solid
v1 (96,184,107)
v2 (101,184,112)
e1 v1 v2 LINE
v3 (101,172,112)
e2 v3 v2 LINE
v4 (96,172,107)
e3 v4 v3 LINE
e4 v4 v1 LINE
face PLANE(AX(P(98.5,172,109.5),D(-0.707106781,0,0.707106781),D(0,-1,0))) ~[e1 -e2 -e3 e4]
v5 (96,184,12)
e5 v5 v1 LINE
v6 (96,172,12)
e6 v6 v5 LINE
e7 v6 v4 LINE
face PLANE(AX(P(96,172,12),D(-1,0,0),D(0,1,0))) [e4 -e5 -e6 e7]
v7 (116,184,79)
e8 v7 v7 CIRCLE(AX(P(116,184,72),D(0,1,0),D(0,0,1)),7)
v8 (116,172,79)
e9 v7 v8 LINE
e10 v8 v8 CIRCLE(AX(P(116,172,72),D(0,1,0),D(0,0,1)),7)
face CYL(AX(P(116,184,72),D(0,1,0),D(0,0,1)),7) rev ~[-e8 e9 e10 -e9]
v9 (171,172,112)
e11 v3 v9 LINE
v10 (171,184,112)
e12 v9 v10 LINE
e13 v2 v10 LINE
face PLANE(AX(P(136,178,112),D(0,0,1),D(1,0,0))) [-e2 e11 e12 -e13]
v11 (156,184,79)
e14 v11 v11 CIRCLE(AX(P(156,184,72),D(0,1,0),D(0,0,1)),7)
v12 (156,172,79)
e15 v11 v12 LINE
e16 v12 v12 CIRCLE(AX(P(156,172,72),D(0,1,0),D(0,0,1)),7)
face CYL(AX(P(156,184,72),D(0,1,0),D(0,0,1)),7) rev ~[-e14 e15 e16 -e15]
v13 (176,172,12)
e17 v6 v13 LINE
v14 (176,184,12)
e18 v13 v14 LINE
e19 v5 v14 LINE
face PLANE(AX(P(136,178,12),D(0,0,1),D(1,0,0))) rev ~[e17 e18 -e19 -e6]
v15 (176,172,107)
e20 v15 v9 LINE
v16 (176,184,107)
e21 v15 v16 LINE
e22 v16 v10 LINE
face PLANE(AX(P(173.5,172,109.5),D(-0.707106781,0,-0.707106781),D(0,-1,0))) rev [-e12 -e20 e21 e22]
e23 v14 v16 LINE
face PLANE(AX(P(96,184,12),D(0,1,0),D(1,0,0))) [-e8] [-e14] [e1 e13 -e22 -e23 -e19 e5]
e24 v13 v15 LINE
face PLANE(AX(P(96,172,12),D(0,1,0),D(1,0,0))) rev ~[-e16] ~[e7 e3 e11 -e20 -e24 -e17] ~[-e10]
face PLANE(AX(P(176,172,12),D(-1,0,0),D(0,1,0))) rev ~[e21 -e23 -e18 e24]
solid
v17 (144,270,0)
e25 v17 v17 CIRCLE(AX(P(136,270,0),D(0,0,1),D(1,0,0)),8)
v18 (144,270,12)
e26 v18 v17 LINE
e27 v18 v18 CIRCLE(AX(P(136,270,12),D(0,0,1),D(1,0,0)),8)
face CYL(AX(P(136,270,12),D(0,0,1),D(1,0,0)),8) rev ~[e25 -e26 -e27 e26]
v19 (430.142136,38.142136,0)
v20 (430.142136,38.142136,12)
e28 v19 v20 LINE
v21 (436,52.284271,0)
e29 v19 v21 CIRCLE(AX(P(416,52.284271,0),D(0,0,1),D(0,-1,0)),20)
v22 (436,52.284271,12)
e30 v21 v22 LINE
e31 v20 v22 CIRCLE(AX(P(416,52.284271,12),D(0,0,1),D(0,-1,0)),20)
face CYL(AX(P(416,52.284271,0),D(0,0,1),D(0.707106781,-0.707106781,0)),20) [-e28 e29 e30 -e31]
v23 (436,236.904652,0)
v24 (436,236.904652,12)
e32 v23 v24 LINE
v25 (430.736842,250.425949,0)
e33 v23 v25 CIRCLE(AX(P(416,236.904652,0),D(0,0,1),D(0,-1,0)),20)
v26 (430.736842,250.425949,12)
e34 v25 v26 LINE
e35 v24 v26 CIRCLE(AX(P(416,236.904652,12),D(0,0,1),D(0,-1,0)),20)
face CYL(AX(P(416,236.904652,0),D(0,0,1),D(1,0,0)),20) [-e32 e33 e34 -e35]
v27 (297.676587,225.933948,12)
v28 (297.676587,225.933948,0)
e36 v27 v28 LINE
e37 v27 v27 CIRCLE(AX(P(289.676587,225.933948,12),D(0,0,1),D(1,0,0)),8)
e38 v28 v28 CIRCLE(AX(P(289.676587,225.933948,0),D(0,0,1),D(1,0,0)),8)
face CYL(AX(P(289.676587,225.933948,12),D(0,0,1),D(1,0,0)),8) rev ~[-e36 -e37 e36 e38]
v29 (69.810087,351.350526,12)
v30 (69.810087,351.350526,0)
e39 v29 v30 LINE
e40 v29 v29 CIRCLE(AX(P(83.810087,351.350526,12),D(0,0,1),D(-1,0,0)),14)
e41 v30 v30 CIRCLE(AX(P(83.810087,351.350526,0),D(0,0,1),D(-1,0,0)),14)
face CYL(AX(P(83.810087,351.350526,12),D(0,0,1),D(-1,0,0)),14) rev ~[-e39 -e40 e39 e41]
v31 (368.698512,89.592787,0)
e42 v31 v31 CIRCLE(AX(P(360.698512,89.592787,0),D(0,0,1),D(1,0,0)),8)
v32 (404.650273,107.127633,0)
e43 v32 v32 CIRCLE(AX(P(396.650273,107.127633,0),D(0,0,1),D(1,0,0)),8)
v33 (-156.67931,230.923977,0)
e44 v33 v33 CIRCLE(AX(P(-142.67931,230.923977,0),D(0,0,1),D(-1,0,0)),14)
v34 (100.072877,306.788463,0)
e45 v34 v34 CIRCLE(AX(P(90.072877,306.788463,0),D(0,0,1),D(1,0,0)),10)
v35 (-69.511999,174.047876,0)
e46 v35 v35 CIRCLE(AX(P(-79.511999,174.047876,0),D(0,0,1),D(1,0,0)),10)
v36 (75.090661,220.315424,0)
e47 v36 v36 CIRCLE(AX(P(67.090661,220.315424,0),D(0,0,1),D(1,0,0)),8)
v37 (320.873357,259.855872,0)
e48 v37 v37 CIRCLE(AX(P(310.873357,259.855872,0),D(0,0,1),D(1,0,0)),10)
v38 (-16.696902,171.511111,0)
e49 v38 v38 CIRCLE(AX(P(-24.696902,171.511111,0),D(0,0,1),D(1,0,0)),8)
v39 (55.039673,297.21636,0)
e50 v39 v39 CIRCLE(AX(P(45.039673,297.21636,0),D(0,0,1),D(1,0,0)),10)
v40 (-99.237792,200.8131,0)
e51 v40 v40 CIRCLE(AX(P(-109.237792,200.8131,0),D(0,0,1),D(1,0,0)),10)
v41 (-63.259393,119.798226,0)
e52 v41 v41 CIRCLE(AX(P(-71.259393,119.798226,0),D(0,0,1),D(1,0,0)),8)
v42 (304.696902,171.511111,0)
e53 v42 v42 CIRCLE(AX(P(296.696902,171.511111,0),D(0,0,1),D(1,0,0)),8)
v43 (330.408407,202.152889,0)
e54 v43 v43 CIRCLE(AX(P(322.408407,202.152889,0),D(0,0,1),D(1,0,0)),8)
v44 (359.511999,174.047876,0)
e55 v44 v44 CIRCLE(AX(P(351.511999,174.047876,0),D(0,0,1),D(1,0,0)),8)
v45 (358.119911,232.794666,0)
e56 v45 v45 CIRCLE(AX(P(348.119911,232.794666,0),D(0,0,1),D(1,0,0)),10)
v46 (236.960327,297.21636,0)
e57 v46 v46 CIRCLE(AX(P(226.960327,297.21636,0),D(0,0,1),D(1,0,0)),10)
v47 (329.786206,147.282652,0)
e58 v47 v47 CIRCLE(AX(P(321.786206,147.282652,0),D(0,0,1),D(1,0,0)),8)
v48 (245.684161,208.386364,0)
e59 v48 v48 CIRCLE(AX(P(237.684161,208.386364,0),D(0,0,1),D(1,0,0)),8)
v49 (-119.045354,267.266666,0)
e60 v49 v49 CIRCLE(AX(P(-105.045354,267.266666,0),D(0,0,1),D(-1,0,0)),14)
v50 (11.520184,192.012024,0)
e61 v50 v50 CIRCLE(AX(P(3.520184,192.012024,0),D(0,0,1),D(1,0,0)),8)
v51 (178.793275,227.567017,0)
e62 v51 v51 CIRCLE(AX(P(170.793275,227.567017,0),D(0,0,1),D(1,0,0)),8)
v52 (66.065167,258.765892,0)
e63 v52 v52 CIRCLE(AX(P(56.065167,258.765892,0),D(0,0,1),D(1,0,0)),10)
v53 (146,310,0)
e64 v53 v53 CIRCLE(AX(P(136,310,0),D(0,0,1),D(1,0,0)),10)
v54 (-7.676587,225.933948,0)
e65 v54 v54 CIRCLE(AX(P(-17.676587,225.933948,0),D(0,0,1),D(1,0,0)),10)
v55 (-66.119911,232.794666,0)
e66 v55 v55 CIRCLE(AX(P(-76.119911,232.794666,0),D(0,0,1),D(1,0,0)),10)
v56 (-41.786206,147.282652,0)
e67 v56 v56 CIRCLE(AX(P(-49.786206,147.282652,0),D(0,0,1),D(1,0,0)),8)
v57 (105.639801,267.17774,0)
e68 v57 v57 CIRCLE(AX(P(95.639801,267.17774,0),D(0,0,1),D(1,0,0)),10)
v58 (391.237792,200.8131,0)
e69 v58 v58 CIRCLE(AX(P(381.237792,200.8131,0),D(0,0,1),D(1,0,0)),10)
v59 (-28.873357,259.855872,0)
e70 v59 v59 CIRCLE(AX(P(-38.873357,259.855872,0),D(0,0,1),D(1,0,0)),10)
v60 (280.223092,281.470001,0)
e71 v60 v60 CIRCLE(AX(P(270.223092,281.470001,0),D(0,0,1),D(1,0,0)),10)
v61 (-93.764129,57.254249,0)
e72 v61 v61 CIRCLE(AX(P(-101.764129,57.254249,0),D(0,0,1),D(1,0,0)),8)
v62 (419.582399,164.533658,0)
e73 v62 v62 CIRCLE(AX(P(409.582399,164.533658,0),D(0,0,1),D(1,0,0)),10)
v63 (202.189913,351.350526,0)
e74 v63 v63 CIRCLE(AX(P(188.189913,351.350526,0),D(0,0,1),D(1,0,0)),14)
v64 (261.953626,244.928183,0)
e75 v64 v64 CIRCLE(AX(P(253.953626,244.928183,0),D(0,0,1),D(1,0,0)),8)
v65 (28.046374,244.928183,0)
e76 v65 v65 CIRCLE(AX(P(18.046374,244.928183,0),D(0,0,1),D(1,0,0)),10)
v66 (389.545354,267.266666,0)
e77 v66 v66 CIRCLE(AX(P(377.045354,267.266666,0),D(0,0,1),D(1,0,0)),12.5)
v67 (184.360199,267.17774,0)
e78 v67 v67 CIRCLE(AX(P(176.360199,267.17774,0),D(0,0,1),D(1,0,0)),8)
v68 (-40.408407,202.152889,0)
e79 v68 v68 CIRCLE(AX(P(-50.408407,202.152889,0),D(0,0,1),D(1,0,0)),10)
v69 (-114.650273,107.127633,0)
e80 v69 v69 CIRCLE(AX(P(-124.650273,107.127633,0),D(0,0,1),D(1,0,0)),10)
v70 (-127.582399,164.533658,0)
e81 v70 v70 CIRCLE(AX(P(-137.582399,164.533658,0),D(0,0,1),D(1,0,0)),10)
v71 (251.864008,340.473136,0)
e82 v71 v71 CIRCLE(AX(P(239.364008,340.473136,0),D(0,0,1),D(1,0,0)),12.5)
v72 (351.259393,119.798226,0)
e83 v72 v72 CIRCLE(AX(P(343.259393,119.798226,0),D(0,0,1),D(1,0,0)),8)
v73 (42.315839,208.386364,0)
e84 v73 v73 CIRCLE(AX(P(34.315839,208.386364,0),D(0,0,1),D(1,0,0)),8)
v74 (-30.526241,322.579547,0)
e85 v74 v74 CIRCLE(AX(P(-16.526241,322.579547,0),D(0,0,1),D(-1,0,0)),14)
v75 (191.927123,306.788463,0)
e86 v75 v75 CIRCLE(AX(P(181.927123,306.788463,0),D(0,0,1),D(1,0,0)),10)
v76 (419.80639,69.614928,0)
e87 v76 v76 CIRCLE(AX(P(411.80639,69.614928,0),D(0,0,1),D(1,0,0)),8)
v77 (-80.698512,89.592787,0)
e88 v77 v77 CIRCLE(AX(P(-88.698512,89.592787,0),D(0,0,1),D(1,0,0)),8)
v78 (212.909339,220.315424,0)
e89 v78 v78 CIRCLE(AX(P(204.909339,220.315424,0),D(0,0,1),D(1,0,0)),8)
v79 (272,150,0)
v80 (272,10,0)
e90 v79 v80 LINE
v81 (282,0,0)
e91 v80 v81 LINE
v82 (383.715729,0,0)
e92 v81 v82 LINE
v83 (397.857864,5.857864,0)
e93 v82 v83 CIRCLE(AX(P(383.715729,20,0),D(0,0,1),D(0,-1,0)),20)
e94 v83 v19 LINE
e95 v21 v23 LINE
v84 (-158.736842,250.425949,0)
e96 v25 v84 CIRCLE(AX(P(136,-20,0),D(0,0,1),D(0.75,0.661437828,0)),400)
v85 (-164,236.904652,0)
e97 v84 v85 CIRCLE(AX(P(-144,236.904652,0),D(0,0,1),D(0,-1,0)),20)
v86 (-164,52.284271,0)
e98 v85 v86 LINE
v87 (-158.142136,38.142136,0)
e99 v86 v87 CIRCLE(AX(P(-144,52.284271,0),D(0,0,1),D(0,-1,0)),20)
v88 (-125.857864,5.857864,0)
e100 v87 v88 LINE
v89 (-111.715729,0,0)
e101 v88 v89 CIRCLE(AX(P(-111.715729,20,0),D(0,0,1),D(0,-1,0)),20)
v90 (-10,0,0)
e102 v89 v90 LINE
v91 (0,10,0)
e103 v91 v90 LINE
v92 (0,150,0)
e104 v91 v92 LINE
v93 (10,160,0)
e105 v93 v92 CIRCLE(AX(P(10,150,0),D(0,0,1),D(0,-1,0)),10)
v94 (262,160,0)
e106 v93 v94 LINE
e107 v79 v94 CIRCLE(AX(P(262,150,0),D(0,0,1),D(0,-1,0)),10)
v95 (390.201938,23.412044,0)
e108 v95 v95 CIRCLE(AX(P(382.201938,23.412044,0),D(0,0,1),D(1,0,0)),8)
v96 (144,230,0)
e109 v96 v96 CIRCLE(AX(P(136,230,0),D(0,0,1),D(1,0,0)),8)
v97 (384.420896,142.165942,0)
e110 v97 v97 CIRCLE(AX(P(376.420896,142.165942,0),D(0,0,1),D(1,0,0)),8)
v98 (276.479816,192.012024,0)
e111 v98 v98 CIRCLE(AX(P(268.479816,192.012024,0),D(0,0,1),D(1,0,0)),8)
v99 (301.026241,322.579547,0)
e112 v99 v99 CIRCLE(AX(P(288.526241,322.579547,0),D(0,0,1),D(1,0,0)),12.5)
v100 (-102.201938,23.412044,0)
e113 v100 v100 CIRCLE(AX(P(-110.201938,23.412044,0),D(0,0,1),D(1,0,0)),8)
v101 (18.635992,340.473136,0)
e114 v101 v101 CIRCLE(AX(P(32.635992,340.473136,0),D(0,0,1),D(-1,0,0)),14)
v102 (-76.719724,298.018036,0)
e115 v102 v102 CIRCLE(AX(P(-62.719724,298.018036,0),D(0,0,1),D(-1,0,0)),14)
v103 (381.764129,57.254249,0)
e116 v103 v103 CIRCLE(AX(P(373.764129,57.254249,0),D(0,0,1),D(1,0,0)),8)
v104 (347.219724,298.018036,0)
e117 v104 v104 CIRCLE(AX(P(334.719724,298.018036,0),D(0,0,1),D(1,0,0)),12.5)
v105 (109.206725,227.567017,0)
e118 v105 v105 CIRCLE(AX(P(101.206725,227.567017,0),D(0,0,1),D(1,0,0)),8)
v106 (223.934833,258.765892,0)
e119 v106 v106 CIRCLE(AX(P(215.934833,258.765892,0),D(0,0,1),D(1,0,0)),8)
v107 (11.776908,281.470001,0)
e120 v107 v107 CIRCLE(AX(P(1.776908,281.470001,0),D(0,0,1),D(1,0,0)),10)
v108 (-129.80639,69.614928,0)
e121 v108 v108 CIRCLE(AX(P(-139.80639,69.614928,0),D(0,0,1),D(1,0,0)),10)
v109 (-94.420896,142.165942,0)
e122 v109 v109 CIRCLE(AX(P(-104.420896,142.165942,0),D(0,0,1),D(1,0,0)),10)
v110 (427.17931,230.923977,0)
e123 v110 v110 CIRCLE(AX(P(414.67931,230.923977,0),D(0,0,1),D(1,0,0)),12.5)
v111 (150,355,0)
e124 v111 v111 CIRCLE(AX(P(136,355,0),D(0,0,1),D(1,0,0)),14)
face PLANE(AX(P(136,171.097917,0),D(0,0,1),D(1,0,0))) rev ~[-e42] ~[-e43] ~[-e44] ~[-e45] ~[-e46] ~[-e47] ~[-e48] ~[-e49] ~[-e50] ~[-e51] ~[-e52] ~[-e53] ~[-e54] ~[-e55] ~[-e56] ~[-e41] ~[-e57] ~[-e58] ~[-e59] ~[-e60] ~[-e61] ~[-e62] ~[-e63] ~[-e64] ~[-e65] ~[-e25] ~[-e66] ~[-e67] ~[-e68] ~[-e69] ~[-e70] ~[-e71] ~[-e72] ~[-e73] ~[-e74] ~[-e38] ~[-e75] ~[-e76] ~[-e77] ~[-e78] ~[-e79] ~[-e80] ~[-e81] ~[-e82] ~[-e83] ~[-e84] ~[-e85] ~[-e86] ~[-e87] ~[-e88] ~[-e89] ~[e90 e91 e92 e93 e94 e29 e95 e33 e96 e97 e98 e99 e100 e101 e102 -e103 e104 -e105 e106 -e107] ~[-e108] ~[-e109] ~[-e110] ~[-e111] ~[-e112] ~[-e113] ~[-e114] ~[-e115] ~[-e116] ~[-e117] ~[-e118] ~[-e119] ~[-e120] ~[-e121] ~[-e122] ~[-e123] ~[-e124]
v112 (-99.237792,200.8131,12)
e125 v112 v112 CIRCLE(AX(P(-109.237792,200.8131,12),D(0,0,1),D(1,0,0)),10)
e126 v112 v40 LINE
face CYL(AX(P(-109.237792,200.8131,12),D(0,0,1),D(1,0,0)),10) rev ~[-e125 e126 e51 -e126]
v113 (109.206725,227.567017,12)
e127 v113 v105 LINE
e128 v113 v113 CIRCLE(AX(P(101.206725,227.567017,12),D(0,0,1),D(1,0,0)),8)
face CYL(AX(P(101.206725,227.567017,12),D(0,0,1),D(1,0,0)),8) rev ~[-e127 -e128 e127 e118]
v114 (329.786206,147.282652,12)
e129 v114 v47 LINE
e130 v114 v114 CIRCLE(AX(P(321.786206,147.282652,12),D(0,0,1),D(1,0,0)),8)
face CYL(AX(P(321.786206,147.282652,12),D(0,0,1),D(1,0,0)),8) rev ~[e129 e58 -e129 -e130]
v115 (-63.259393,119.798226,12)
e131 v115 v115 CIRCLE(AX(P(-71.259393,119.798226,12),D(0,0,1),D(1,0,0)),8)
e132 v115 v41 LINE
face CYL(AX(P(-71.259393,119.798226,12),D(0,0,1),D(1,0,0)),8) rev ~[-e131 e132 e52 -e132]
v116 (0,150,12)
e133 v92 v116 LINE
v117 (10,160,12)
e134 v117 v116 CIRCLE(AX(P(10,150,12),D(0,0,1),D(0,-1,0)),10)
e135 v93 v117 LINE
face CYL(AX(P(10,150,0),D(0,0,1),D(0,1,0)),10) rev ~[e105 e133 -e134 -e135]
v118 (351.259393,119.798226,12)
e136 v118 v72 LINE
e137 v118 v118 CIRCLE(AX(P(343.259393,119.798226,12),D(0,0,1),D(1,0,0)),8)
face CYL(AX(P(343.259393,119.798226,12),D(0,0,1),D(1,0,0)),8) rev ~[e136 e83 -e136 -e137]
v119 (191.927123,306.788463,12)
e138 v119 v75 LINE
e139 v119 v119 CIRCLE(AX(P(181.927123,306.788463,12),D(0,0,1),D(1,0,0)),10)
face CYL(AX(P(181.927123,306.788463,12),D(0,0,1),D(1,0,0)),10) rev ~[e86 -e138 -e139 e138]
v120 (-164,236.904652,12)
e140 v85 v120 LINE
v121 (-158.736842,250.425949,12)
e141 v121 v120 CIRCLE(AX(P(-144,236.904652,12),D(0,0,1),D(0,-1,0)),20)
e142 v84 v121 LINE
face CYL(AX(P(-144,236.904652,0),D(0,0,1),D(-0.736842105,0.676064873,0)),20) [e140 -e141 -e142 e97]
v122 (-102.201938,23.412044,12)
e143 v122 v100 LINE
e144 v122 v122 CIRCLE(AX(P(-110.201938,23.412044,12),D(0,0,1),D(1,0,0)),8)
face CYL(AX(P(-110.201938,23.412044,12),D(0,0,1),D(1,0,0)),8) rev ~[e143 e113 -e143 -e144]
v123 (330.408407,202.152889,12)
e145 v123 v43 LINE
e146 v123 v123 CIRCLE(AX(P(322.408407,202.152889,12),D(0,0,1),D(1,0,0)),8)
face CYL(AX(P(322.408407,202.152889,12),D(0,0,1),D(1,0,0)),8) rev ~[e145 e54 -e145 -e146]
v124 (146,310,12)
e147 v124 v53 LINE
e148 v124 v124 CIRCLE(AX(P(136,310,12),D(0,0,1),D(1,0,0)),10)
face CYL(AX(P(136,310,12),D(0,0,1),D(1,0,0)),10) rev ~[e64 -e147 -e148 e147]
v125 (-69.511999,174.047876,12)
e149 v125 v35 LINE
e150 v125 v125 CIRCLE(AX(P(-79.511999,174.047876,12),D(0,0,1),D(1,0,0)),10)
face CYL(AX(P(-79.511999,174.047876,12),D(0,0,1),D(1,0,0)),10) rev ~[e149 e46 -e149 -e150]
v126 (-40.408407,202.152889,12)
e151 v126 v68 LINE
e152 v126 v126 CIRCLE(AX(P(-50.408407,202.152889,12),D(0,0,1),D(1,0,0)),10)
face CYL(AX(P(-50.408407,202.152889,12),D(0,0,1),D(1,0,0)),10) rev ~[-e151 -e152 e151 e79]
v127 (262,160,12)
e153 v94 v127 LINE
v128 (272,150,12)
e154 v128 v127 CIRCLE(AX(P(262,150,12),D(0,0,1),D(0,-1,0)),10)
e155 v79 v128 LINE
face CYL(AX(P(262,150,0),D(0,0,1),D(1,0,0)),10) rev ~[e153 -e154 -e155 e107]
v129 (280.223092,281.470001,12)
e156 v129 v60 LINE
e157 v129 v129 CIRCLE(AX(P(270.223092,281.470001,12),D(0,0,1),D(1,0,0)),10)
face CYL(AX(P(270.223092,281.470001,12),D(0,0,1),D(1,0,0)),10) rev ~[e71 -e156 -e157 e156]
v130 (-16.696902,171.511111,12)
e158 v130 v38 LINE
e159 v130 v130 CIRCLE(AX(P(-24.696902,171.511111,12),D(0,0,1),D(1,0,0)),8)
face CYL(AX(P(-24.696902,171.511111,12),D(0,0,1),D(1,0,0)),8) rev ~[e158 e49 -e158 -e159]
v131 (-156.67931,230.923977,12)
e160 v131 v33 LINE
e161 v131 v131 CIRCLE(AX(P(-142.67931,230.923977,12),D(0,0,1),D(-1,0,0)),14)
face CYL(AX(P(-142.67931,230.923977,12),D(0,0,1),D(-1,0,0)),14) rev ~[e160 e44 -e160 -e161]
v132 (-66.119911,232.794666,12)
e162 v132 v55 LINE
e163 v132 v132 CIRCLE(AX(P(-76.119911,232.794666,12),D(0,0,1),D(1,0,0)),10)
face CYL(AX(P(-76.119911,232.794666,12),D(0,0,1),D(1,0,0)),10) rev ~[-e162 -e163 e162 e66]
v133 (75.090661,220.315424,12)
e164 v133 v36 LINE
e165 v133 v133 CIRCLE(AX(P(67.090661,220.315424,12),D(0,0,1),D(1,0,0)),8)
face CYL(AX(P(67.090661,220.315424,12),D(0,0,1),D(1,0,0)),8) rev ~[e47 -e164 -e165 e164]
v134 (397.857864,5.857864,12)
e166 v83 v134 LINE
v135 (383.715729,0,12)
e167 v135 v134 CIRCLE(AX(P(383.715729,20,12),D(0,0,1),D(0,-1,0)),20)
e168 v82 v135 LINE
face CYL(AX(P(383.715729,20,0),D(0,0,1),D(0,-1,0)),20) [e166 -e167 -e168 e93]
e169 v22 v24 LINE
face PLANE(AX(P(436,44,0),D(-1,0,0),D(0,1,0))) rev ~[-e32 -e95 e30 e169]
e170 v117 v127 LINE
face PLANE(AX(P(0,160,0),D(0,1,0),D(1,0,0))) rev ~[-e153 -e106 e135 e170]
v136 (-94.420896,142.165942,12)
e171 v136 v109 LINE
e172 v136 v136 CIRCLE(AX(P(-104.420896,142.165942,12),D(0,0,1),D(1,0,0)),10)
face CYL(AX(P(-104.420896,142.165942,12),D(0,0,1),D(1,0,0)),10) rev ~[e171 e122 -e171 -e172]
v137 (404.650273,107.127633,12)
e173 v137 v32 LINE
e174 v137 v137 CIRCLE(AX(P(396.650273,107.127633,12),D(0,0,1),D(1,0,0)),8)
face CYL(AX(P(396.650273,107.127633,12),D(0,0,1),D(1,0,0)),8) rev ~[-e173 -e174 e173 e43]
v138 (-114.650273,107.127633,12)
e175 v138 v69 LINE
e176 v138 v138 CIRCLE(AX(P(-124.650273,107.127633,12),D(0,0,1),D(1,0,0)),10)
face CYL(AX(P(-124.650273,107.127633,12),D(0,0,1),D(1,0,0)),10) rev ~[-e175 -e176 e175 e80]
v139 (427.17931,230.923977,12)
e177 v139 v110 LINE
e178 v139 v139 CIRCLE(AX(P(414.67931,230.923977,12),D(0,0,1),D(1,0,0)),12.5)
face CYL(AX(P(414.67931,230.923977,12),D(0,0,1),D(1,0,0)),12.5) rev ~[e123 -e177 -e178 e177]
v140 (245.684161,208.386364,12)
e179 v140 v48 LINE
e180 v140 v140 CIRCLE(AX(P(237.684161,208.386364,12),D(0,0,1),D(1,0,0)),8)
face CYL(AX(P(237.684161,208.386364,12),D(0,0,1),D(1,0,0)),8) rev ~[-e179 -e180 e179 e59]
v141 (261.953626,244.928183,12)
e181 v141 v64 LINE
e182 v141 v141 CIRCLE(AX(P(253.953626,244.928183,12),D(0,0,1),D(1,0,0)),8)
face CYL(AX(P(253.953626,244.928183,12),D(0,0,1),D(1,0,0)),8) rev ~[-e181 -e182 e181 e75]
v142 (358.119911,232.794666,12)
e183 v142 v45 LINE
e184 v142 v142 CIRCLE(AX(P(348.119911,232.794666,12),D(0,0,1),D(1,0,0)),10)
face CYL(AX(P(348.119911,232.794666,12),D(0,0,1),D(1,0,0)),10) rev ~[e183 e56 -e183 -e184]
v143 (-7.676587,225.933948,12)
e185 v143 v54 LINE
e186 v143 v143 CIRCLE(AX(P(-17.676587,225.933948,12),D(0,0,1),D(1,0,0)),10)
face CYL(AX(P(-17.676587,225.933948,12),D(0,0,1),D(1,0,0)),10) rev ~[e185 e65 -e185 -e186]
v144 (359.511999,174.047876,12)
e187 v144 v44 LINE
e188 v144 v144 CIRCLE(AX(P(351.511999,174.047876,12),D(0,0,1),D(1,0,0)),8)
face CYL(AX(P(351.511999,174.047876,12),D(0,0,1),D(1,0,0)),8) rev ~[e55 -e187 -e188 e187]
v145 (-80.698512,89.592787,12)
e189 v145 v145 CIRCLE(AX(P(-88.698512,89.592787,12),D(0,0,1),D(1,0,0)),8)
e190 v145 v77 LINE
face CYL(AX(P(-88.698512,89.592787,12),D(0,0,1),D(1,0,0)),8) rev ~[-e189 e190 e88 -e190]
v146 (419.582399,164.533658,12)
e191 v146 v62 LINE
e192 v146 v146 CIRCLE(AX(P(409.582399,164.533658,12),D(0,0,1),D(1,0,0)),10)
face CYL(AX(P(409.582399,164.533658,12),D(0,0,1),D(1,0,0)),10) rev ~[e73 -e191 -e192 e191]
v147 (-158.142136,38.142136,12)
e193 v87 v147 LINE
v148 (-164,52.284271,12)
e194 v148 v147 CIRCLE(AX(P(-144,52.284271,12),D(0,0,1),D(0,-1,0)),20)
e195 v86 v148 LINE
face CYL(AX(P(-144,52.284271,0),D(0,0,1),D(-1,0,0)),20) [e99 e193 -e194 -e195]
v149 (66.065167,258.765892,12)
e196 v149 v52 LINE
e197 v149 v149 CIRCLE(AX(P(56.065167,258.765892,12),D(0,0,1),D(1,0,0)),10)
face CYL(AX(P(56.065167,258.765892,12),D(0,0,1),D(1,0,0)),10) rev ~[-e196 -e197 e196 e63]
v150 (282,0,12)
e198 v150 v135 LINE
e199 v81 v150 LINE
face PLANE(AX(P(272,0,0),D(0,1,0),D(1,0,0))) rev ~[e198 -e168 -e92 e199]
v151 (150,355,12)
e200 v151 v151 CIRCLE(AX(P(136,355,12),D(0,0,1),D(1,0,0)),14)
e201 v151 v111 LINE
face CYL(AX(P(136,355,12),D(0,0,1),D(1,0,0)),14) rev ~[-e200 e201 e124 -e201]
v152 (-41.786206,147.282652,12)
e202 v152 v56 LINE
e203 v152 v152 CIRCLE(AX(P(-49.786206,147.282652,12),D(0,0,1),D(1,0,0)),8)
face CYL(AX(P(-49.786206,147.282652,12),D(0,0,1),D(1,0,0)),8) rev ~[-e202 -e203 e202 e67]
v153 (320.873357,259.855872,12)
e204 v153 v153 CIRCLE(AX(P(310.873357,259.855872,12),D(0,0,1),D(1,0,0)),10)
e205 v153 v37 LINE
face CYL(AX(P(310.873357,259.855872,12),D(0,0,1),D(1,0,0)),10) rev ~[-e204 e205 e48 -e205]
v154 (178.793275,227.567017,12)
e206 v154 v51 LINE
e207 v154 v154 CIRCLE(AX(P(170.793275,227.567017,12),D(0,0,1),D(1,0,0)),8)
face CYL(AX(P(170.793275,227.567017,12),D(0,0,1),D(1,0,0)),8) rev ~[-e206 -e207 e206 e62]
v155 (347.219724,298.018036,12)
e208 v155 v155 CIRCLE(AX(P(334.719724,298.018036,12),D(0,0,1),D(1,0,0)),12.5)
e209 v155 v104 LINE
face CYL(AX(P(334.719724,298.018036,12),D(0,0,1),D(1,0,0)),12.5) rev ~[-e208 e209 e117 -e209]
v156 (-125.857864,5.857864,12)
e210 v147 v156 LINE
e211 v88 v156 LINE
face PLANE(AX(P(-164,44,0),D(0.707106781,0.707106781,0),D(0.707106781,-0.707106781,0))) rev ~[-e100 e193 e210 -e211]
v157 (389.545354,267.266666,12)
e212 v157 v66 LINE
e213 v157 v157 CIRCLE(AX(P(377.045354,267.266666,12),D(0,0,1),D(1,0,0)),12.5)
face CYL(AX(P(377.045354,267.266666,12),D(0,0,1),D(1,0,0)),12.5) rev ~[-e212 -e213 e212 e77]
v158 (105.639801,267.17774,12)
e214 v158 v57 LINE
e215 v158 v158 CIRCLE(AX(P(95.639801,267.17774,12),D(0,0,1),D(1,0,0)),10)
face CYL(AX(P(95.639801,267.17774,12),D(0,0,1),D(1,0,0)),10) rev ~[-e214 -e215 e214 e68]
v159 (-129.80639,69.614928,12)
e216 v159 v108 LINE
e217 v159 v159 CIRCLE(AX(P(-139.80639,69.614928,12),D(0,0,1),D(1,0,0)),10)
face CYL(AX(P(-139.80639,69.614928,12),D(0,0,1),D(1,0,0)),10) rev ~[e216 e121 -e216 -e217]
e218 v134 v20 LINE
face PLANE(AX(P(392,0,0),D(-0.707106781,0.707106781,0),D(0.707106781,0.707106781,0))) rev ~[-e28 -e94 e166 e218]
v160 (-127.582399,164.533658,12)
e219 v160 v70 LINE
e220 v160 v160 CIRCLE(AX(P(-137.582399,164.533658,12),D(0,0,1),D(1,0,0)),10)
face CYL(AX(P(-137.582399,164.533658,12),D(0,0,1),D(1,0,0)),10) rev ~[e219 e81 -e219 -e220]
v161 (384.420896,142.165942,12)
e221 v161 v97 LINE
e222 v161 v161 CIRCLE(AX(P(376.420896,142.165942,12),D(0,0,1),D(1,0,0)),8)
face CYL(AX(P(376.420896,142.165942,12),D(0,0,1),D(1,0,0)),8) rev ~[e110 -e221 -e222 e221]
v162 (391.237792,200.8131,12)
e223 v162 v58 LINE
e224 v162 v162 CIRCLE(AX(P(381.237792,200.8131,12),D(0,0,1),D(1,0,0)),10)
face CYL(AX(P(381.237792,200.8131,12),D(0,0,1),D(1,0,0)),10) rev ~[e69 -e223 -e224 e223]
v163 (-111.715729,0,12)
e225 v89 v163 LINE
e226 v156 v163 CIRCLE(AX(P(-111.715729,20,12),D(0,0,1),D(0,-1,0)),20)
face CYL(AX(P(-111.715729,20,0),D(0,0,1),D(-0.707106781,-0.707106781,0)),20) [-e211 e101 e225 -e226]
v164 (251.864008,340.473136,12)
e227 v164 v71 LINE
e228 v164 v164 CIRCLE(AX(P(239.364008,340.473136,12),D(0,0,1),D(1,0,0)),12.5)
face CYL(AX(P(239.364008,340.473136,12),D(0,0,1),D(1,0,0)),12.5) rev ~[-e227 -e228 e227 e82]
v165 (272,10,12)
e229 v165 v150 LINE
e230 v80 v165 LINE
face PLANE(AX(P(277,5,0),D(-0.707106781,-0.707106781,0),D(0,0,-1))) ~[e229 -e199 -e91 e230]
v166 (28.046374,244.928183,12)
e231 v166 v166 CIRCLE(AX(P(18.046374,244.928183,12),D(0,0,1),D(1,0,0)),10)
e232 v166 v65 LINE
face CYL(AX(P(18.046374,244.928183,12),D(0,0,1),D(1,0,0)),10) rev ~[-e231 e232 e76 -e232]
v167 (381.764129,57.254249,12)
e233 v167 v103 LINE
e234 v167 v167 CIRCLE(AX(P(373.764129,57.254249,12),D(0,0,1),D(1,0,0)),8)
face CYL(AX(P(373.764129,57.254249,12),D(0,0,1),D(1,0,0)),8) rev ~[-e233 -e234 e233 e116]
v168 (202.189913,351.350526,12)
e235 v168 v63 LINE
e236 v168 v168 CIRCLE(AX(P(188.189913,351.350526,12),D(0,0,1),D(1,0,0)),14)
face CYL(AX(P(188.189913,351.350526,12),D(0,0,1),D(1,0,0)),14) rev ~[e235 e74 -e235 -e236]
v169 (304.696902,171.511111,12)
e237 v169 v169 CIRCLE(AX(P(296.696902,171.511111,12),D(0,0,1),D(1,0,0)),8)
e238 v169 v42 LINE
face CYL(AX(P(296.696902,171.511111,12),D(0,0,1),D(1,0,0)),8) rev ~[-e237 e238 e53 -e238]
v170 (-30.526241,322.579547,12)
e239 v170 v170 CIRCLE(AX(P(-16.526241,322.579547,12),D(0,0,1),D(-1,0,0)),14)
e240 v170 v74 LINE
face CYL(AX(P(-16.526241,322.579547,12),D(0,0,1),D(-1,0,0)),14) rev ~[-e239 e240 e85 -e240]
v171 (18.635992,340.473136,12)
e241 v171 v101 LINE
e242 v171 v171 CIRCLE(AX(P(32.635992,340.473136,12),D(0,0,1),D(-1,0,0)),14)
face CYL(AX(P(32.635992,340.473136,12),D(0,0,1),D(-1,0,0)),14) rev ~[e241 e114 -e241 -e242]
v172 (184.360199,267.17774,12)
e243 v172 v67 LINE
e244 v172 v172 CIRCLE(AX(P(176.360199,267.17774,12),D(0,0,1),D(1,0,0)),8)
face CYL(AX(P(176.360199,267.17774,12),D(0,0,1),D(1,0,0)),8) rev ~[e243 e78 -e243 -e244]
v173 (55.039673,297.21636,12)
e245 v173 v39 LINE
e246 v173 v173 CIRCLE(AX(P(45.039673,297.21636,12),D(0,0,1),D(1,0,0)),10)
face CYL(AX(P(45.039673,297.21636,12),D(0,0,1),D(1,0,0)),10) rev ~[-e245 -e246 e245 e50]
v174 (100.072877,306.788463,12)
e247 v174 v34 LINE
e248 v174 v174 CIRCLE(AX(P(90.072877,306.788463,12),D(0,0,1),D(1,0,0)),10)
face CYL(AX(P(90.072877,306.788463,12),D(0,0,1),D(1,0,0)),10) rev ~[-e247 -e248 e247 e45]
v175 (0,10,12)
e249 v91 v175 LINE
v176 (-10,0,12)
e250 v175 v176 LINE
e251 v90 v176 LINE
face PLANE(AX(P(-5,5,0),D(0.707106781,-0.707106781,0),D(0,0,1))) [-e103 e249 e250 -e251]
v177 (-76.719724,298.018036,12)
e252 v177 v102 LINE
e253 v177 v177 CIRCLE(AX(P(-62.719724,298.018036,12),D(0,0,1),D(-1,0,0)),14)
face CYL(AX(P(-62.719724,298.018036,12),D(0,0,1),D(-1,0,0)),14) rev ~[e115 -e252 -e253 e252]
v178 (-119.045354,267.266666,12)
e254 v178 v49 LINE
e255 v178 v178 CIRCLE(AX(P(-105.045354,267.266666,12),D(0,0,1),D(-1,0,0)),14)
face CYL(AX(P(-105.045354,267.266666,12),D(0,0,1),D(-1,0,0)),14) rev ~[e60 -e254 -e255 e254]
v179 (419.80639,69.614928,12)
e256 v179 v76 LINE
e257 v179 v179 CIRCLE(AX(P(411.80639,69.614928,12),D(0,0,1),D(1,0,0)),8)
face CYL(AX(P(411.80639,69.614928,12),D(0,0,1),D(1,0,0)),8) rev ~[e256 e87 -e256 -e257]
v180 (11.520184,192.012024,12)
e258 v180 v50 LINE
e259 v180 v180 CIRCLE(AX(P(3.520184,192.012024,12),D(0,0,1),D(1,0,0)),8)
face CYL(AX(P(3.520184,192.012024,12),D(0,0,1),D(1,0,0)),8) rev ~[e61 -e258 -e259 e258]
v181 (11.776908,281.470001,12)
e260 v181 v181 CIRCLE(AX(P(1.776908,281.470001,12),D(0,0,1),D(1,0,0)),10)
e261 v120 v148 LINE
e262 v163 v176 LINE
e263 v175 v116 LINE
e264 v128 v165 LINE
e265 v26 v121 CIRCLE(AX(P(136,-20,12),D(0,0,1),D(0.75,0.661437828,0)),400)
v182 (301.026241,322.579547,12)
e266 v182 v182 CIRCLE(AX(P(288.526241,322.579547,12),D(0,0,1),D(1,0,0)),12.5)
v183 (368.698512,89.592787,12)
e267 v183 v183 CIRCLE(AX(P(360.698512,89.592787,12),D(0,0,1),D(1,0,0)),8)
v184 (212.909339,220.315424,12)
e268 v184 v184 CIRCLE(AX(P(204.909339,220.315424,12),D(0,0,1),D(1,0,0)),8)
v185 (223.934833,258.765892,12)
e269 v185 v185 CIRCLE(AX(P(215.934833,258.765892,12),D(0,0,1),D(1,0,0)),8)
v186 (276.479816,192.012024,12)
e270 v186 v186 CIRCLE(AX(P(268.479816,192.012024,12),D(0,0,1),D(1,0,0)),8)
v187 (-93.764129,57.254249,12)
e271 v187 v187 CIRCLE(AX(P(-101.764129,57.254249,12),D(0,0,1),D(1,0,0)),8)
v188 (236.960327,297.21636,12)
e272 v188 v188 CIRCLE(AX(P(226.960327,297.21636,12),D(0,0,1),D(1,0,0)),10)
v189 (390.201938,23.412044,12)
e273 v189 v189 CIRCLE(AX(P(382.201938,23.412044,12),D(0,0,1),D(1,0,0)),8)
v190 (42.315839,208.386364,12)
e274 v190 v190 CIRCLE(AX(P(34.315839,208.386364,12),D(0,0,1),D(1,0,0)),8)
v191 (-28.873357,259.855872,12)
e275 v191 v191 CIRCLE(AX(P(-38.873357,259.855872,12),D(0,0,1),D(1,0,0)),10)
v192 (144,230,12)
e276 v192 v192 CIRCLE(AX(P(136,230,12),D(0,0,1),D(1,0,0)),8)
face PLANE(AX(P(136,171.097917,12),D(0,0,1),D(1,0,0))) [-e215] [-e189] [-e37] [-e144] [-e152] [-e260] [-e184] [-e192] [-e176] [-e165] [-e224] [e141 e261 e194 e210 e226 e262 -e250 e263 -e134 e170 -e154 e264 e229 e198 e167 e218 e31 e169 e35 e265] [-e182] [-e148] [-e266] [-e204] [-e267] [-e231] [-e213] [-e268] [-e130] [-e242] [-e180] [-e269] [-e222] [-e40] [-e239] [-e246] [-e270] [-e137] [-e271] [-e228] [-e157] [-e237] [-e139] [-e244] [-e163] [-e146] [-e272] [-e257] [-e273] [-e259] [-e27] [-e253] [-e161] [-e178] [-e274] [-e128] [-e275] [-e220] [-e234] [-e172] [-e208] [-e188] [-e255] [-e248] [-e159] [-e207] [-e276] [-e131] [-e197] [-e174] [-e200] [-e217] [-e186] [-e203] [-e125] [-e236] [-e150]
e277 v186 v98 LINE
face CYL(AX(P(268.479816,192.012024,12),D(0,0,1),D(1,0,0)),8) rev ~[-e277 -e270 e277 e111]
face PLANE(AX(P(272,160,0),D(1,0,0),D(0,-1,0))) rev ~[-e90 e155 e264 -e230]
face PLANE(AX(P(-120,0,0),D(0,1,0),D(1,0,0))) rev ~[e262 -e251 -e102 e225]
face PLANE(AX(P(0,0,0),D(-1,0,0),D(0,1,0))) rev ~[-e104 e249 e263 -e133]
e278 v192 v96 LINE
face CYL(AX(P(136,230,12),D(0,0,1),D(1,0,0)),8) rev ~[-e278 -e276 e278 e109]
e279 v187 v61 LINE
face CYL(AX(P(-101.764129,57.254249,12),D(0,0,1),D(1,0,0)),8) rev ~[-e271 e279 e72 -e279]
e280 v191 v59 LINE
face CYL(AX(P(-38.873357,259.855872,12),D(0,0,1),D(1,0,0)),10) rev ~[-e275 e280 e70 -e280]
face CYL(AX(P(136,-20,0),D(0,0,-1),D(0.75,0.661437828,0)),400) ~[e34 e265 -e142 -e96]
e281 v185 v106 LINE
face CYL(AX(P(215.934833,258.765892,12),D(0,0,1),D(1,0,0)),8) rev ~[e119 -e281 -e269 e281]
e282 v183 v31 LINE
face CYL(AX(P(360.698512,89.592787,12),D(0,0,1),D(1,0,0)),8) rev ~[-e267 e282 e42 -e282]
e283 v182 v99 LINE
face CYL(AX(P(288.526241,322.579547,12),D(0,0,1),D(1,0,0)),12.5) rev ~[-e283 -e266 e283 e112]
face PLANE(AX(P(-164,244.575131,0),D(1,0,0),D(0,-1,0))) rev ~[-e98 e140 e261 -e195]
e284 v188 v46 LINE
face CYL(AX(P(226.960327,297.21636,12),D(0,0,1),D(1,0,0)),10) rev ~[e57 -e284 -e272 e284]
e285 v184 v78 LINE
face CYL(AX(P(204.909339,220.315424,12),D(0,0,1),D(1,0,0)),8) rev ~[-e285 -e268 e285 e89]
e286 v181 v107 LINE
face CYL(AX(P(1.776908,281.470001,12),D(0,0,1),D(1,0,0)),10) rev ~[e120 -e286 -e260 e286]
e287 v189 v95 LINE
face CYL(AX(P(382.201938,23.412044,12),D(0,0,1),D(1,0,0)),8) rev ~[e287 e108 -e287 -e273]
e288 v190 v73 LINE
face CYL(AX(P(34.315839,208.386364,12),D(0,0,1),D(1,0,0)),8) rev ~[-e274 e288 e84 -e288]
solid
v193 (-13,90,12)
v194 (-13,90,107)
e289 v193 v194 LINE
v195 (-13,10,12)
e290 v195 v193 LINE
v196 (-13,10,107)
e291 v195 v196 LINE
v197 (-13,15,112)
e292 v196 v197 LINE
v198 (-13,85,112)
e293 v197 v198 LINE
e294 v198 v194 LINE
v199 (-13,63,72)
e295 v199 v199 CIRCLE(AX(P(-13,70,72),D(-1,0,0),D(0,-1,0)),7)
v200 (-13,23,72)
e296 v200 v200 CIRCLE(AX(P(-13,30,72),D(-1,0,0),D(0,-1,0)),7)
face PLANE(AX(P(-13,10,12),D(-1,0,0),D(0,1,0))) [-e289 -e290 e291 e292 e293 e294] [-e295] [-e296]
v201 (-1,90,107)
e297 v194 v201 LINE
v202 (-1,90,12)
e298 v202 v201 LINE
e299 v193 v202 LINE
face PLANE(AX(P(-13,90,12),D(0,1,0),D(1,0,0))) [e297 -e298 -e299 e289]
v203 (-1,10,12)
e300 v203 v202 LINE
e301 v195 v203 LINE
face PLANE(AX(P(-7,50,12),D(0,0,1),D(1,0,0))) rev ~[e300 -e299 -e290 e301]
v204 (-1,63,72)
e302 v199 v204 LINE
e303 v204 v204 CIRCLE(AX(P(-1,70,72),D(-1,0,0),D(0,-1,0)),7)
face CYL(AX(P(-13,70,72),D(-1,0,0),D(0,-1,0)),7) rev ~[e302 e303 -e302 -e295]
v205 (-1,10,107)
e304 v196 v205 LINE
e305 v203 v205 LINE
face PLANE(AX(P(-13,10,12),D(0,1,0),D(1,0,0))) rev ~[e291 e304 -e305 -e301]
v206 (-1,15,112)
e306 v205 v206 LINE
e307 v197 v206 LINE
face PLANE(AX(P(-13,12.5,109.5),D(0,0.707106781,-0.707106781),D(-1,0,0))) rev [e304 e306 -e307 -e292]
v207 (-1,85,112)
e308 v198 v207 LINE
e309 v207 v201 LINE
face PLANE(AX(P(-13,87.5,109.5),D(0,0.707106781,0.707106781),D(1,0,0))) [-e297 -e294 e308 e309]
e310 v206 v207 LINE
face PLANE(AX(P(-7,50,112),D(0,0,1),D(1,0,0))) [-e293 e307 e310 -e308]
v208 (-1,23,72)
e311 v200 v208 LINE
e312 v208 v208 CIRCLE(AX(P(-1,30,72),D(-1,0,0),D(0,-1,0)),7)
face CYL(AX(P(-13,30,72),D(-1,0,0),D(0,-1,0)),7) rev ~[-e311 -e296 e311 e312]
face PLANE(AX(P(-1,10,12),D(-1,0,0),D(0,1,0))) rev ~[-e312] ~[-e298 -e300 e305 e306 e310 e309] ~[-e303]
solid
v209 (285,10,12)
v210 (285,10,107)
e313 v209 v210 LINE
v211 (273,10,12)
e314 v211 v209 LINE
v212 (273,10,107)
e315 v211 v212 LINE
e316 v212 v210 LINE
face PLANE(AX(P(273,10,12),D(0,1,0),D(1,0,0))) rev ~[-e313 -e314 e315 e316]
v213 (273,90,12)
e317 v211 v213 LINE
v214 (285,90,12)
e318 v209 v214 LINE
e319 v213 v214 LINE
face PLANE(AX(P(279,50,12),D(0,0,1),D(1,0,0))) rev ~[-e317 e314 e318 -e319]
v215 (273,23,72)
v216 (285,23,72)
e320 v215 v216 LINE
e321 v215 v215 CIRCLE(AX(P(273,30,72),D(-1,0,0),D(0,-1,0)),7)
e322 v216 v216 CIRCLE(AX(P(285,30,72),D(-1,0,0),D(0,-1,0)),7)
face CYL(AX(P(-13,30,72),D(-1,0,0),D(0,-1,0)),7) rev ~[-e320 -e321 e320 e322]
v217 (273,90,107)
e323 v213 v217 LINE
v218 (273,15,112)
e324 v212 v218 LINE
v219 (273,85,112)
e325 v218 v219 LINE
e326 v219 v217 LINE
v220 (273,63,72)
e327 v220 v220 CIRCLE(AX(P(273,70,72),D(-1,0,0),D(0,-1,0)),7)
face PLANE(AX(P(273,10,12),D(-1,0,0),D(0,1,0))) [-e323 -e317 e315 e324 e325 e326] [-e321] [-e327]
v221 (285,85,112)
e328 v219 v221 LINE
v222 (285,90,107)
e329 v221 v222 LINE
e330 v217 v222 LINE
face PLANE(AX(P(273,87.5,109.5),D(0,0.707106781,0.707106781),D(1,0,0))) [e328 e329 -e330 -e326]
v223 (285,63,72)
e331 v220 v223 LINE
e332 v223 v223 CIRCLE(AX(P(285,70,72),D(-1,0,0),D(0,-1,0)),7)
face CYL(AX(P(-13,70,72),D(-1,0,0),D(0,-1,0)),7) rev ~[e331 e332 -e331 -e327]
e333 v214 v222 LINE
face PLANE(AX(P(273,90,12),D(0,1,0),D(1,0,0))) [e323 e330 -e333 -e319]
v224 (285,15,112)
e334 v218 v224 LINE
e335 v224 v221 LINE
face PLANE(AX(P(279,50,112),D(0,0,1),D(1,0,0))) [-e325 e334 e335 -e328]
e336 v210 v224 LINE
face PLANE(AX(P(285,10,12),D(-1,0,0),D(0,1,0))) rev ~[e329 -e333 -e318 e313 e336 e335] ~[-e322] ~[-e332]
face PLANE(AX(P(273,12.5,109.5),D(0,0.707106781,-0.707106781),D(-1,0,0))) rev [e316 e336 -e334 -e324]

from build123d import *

# Parameters (mm, degrees)
EXTRUDE_1_DEPTH     = 12
FILLET_1_R          = 20
FILLET_2_R          = 10
SKETCH_2_W          = 12
SKETCH_2_H          = 80
EXTRUDE_2_DEPTH     = 100
EXTRUDE_2_2_DEPTH   = 100
SKETCH_2_W_2        = 80
SKETCH_2_H_2        = 12
EXTRUDE_2_3_DEPTH   = 100
SKETCH_3_R          = 7
CUT_EXTRUDE_1_DEPTH = 599.786272388
CHAMFER_1_SIZE      = 5
CHAMFER_2_SIZE      = 5
CHAMFER_3_SIZE      = 5
SKETCH_4_R          = 7
CUT_EXTRUDE_2_DEPTH = 491.974541091
SKETCH_5_R          = 14
SKETCH_5_R_2        = 12.5
CUT_EXTRUDE_3_DEPTH = 587.937816127
SKETCH_6_R          = 10
CUT_EXTRUDE_4_DEPTH = 50
SKETCH_7_R          = 8
SKETCH_7_R_2        = 10
CUT_EXTRUDE_5_DEPTH = 587.937816127
SKETCH_8_R          = 8
CUT_EXTRUDE_6_DEPTH = 50
CHAMFER_4_SIZE      = 10


with BuildPart() as part:
    # 草图1 → 凸台-拉伸1 (new body)
    with BuildSketch(Plane.XY):
        with BuildLine():
            Line((0, 0), (0, 160))
            Line((0, 160), (272, 160))
            Line((272, 160), (272, 0))
            Line((272, 0), (392, 0))
            Line((392, 0), (436, 44))
            Line((436, 44), (436, 244.575131106))
            ThreePointArc((436, 244.575131106), (136, 380), (-164, 244.575131106))
            Line((-164, 244.575131106), (-164, 44))
            Line((-164, 44), (-120, 0))
            Line((-120, 0), (0, 0))
        make_face()
    extrude(amount=EXTRUDE_1_DEPTH)

    # 圆角1
    fillet_1_edges = [part.edges().sort_by_distance(p)[0] for p in [
        (-120, 0, 6),
        (-164, 44, 6),
        (-164, 244.575131106, 6),
        (436, 244.575131106, 6),
        (436, 44, 6),
        (392, 0, 6),
    ]]
    fillet(fillet_1_edges, radius=FILLET_1_R)

    # 圆角2
    fillet_2_edges = [part.edges().sort_by_distance(p)[0] for p in [
        (272, 160, 6),
        (0, 160, 6),
    ]]
    fillet(fillet_2_edges, radius=FILLET_2_R)

    # 草图5 → 切除-拉伸3 (cut, through all)
    with BuildSketch(Plane.XY.offset(12)):
        with Locations((136, 355)):
            Circle(SKETCH_5_R)
        with Locations((188.18991286, 351.350525778)):
            Circle(SKETCH_5_R)
        with Locations(Location((-142.679309554, 230.923977385, 0), (0, 0, 180))):
            Circle(SKETCH_5_R)
        with Locations(Location((-105.045353632, 267.26666617, 0), (0, 0, 180))):
            Circle(SKETCH_5_R)
        with Locations(Location((-62.719724087, 298.018036059, 0), (0, 0, 180))):
            Circle(SKETCH_5_R)
        with Locations(Location((-16.526241153, 322.579546616, 0), (0, 0, 180))):
            Circle(SKETCH_5_R)
        with Locations(Location((32.635991569, 340.473135977, 0), (0, 0, 180))):
            Circle(SKETCH_5_R)
        with Locations(Location((83.81008714, 351.350525778, 0), (0, 0, 180))):
            Circle(SKETCH_5_R)
        with Locations((239.364008431, 340.473135977)):
            Circle(SKETCH_5_R_2)
        with Locations((288.526241153, 322.579546616)):
            Circle(SKETCH_5_R_2)
        with Locations((334.719724087, 298.018036059)):
            Circle(SKETCH_5_R_2)
        with Locations((377.045353632, 267.26666617)):
            Circle(SKETCH_5_R_2)
        with Locations((414.679309554, 230.923977385)):
            Circle(SKETCH_5_R_2)
    extrude(amount=-CUT_EXTRUDE_3_DEPTH, mode=Mode.SUBTRACT)

    # 草图6 → 切除-拉伸4 (cut)
    with BuildSketch(Plane.XY.offset(12)):
        with Locations((136, 310)):
            Circle(SKETCH_6_R)
        with Locations((181.927123317, 306.788462685)):
            Circle(SKETCH_6_R)
        with Locations((226.96032742, 297.21635966)):
            Circle(SKETCH_6_R)
        with Locations((270.223092215, 281.470001022)):
            Circle(SKETCH_6_R)
        with Locations((310.873357197, 259.855871732)):
            Circle(SKETCH_6_R)
        with Locations((348.119911197, 232.794666229)):
            Circle(SKETCH_6_R)
        with Locations((381.237792408, 200.813100098)):
            Circle(SKETCH_6_R)
        with Locations((-109.237792408, 200.813100098)):
            Circle(SKETCH_6_R)
        with Locations((-76.119911197, 232.794666229)):
            Circle(SKETCH_6_R)
        with Locations((-38.873357197, 259.855871732)):
            Circle(SKETCH_6_R)
        with Locations((1.776907785, 281.470001022)):
            Circle(SKETCH_6_R)
        with Locations((45.03967258, 297.21635966)):
            Circle(SKETCH_6_R)
        with Locations((90.072876683, 306.788462685)):
            Circle(SKETCH_6_R)
        with Locations((409.582398943, 164.533658145)):
            Circle(SKETCH_6_R)
        with Locations((-137.582398943, 164.533658145)):
            Circle(SKETCH_6_R)
    extrude(amount=-CUT_EXTRUDE_4_DEPTH, mode=Mode.SUBTRACT)

    # 草图7 → 切除-拉伸5 (cut, through all)
    with BuildSketch(Plane.XY.offset(12)):
        with Locations((136, 270)):
            Circle(SKETCH_7_R)
        with Locations((176.360199278, 267.177739935)):
            Circle(SKETCH_7_R)
        with Locations((215.934833187, 258.765891822)):
            Circle(SKETCH_7_R)
        with Locations((253.953626492, 244.928182716)):
            Circle(SKETCH_7_R)
        with Locations((289.676586628, 225.933947885)):
            Circle(SKETCH_7_R)
        with Locations((322.408406809, 202.152888505)):
            Circle(SKETCH_7_R)
        with Locations((351.511999388, 174.047875844)):
            Circle(SKETCH_7_R)
        with Locations((376.420896041, 142.165942007)):
            Circle(SKETCH_7_R)
        with Locations((396.650273427, 107.127632569)):
            Circle(SKETCH_7_R)
        with Locations((411.806389726, 69.614928369)):
            Circle(SKETCH_7_R)
        with Locations((95.639800722, 267.177739935)):
            Circle(SKETCH_7_R_2)
        with Locations((56.065166813, 258.765891822)):
            Circle(SKETCH_7_R_2)
        with Locations((18.046373508, 244.928182716)):
            Circle(SKETCH_7_R_2)
        with Locations((-17.676586628, 225.933947885)):
            Circle(SKETCH_7_R_2)
        with Locations((-50.408406809, 202.152888505)):
            Circle(SKETCH_7_R_2)
        with Locations((-79.511999388, 174.047875844)):
            Circle(SKETCH_7_R_2)
        with Locations((-104.420896041, 142.165942007)):
            Circle(SKETCH_7_R_2)
        with Locations((-124.650273427, 107.127632569)):
            Circle(SKETCH_7_R_2)
        with Locations((-139.806389726, 69.614928369)):
            Circle(SKETCH_7_R_2)
    extrude(amount=-CUT_EXTRUDE_5_DEPTH, mode=Mode.SUBTRACT)

    # 草图8 → 切除-拉伸6 (cut)
    with BuildSketch(Plane.XY.offset(12)):
        with Locations((136, 230)):
            Circle(SKETCH_8_R)
        with Locations((170.79327524, 227.567017185)):
            Circle(SKETCH_8_R)
        with Locations((204.909338954, 220.315423985)):
            Circle(SKETCH_8_R)
        with Locations((237.684160769, 208.386364411)):
            Circle(SKETCH_8_R)
        with Locations((268.479816058, 192.012024039)):
            Circle(SKETCH_8_R)
        with Locations((296.696902422, 171.51111078)):
            Circle(SKETCH_8_R)
        with Locations((321.786206369, 147.28265159)):
            Circle(SKETCH_8_R)
        with Locations((343.259393139, 119.798225868)):
            Circle(SKETCH_8_R)
        with Locations((360.698511575, 89.592786697)):
            Circle(SKETCH_8_R)
        with Locations((373.764129074, 57.254248594)):
            Circle(SKETCH_8_R)
        with Locations((382.201938253, 23.412044417)):
            Circle(SKETCH_8_R)
        with Locations((-110.201938253, 23.412044417)):
            Circle(SKETCH_8_R)
        with Locations((-101.764129074, 57.254248594)):
            Circle(SKETCH_8_R)
        with Locations((-88.698511575, 89.592786697)):
            Circle(SKETCH_8_R)
        with Locations((-71.259393139, 119.798225868)):
            Circle(SKETCH_8_R)
        with Locations((-49.786206369, 147.28265159)):
            Circle(SKETCH_8_R)
        with Locations((-24.696902422, 171.51111078)):
            Circle(SKETCH_8_R)
        with Locations((3.520183942, 192.012024039)):
            Circle(SKETCH_8_R)
        with Locations((34.315839231, 208.386364411)):
            Circle(SKETCH_8_R)
        with Locations((67.090661046, 220.315423985)):
            Circle(SKETCH_8_R)
        with Locations((101.20672476, 227.567017185)):
            Circle(SKETCH_8_R)
    extrude(amount=-CUT_EXTRUDE_6_DEPTH, mode=Mode.SUBTRACT)

    # 倒角4
    chamfer_4_edges = [part.edges().sort_by_distance(p)[0] for p in [
        (272, 0, 6),
        (0, 0, 6),
    ]]
    chamfer(chamfer_4_edges, length=CHAMFER_4_SIZE)


with BuildPart() as body_2:
    # 草图2 → 凸台-拉伸2 (new body)
    with BuildSketch(Plane.XY.offset(12)):
        with Locations((-7, 50)):
            Rectangle(SKETCH_2_W, SKETCH_2_H)
    extrude(amount=EXTRUDE_2_DEPTH)


with BuildPart() as body_3:
    # 草图2 → Extrude 2 2 (new body)
    with BuildSketch(Plane.XY.offset(12)):
        with Locations((279, 50)):
            Rectangle(SKETCH_2_W, SKETCH_2_H)
    extrude(amount=EXTRUDE_2_2_DEPTH)


with BuildPart() as body_4:
    # 草图2 → Extrude 2 3 (new body)
    with BuildSketch(Plane.XY.offset(12)):
        with Locations((136, 178)):
            Rectangle(SKETCH_2_W_2, SKETCH_2_H_2)
    extrude(amount=EXTRUDE_2_3_DEPTH)

    # 倒角3
    chamfer_3_edges = [body_4.edges().sort_by_distance(p)[0] for p in [
        (96, 178, 112),
        (176, 178, 112),
    ]]
    chamfer(chamfer_3_edges, length=CHAMFER_3_SIZE)

    # 草图4 → 切除-拉伸2 (cut, through all)
    with BuildSketch(Plane(origin=(0, 184, 0), x_dir=(1, 0, 0), z_dir=(0, 1, 0))):
        with Locations(Location((116, -72, 0), (0, 0, 270))):
            Circle(SKETCH_4_R)
        with Locations(Location((156, -72, 0), (0, 0, 270))):
            Circle(SKETCH_4_R)
    extrude(amount=-CUT_EXTRUDE_2_DEPTH, mode=Mode.SUBTRACT)


with BuildPart() as cut_extrude_1_tool:
    # 草图3 → 切除-拉伸1 (new, through all)
    with BuildSketch(Plane.ZY.offset(13)):
        with Locations(Location((72, 70, 0), (0, 0, 270))):
            Circle(SKETCH_3_R)
        with Locations(Location((72, 30, 0), (0, 0, 270))):
            Circle(SKETCH_3_R)
    extrude(amount=-CUT_EXTRUDE_1_DEPTH)


with BuildPart() as body_2_1:
    add(body_2.part)

    # 切除-拉伸1: cut by cut_extrude_1_tool
    add(cut_extrude_1_tool.part, mode=Mode.SUBTRACT)

    # 倒角1
    chamfer_1_edges = [body_2_1.edges().sort_by_distance(p)[0] for p in [
        (-7, 10, 112),
        (-7, 90, 112),
    ]]
    chamfer(chamfer_1_edges, length=CHAMFER_1_SIZE)


with BuildPart() as body_3_1:
    add(body_3.part)

    # 切除-拉伸1: cut by cut_extrude_1_tool
    add(cut_extrude_1_tool.part, mode=Mode.SUBTRACT)

    # 倒角2
    chamfer_2_edges = [body_3_1.edges().sort_by_distance(p)[0] for p in [
        (279, 10, 112),
        (279, 90, 112),
    ]]
    chamfer(chamfer_2_edges, length=CHAMFER_2_SIZE)


solid = Compound([part.part, body_4.part, body_2_1.part, body_3_1.part])
